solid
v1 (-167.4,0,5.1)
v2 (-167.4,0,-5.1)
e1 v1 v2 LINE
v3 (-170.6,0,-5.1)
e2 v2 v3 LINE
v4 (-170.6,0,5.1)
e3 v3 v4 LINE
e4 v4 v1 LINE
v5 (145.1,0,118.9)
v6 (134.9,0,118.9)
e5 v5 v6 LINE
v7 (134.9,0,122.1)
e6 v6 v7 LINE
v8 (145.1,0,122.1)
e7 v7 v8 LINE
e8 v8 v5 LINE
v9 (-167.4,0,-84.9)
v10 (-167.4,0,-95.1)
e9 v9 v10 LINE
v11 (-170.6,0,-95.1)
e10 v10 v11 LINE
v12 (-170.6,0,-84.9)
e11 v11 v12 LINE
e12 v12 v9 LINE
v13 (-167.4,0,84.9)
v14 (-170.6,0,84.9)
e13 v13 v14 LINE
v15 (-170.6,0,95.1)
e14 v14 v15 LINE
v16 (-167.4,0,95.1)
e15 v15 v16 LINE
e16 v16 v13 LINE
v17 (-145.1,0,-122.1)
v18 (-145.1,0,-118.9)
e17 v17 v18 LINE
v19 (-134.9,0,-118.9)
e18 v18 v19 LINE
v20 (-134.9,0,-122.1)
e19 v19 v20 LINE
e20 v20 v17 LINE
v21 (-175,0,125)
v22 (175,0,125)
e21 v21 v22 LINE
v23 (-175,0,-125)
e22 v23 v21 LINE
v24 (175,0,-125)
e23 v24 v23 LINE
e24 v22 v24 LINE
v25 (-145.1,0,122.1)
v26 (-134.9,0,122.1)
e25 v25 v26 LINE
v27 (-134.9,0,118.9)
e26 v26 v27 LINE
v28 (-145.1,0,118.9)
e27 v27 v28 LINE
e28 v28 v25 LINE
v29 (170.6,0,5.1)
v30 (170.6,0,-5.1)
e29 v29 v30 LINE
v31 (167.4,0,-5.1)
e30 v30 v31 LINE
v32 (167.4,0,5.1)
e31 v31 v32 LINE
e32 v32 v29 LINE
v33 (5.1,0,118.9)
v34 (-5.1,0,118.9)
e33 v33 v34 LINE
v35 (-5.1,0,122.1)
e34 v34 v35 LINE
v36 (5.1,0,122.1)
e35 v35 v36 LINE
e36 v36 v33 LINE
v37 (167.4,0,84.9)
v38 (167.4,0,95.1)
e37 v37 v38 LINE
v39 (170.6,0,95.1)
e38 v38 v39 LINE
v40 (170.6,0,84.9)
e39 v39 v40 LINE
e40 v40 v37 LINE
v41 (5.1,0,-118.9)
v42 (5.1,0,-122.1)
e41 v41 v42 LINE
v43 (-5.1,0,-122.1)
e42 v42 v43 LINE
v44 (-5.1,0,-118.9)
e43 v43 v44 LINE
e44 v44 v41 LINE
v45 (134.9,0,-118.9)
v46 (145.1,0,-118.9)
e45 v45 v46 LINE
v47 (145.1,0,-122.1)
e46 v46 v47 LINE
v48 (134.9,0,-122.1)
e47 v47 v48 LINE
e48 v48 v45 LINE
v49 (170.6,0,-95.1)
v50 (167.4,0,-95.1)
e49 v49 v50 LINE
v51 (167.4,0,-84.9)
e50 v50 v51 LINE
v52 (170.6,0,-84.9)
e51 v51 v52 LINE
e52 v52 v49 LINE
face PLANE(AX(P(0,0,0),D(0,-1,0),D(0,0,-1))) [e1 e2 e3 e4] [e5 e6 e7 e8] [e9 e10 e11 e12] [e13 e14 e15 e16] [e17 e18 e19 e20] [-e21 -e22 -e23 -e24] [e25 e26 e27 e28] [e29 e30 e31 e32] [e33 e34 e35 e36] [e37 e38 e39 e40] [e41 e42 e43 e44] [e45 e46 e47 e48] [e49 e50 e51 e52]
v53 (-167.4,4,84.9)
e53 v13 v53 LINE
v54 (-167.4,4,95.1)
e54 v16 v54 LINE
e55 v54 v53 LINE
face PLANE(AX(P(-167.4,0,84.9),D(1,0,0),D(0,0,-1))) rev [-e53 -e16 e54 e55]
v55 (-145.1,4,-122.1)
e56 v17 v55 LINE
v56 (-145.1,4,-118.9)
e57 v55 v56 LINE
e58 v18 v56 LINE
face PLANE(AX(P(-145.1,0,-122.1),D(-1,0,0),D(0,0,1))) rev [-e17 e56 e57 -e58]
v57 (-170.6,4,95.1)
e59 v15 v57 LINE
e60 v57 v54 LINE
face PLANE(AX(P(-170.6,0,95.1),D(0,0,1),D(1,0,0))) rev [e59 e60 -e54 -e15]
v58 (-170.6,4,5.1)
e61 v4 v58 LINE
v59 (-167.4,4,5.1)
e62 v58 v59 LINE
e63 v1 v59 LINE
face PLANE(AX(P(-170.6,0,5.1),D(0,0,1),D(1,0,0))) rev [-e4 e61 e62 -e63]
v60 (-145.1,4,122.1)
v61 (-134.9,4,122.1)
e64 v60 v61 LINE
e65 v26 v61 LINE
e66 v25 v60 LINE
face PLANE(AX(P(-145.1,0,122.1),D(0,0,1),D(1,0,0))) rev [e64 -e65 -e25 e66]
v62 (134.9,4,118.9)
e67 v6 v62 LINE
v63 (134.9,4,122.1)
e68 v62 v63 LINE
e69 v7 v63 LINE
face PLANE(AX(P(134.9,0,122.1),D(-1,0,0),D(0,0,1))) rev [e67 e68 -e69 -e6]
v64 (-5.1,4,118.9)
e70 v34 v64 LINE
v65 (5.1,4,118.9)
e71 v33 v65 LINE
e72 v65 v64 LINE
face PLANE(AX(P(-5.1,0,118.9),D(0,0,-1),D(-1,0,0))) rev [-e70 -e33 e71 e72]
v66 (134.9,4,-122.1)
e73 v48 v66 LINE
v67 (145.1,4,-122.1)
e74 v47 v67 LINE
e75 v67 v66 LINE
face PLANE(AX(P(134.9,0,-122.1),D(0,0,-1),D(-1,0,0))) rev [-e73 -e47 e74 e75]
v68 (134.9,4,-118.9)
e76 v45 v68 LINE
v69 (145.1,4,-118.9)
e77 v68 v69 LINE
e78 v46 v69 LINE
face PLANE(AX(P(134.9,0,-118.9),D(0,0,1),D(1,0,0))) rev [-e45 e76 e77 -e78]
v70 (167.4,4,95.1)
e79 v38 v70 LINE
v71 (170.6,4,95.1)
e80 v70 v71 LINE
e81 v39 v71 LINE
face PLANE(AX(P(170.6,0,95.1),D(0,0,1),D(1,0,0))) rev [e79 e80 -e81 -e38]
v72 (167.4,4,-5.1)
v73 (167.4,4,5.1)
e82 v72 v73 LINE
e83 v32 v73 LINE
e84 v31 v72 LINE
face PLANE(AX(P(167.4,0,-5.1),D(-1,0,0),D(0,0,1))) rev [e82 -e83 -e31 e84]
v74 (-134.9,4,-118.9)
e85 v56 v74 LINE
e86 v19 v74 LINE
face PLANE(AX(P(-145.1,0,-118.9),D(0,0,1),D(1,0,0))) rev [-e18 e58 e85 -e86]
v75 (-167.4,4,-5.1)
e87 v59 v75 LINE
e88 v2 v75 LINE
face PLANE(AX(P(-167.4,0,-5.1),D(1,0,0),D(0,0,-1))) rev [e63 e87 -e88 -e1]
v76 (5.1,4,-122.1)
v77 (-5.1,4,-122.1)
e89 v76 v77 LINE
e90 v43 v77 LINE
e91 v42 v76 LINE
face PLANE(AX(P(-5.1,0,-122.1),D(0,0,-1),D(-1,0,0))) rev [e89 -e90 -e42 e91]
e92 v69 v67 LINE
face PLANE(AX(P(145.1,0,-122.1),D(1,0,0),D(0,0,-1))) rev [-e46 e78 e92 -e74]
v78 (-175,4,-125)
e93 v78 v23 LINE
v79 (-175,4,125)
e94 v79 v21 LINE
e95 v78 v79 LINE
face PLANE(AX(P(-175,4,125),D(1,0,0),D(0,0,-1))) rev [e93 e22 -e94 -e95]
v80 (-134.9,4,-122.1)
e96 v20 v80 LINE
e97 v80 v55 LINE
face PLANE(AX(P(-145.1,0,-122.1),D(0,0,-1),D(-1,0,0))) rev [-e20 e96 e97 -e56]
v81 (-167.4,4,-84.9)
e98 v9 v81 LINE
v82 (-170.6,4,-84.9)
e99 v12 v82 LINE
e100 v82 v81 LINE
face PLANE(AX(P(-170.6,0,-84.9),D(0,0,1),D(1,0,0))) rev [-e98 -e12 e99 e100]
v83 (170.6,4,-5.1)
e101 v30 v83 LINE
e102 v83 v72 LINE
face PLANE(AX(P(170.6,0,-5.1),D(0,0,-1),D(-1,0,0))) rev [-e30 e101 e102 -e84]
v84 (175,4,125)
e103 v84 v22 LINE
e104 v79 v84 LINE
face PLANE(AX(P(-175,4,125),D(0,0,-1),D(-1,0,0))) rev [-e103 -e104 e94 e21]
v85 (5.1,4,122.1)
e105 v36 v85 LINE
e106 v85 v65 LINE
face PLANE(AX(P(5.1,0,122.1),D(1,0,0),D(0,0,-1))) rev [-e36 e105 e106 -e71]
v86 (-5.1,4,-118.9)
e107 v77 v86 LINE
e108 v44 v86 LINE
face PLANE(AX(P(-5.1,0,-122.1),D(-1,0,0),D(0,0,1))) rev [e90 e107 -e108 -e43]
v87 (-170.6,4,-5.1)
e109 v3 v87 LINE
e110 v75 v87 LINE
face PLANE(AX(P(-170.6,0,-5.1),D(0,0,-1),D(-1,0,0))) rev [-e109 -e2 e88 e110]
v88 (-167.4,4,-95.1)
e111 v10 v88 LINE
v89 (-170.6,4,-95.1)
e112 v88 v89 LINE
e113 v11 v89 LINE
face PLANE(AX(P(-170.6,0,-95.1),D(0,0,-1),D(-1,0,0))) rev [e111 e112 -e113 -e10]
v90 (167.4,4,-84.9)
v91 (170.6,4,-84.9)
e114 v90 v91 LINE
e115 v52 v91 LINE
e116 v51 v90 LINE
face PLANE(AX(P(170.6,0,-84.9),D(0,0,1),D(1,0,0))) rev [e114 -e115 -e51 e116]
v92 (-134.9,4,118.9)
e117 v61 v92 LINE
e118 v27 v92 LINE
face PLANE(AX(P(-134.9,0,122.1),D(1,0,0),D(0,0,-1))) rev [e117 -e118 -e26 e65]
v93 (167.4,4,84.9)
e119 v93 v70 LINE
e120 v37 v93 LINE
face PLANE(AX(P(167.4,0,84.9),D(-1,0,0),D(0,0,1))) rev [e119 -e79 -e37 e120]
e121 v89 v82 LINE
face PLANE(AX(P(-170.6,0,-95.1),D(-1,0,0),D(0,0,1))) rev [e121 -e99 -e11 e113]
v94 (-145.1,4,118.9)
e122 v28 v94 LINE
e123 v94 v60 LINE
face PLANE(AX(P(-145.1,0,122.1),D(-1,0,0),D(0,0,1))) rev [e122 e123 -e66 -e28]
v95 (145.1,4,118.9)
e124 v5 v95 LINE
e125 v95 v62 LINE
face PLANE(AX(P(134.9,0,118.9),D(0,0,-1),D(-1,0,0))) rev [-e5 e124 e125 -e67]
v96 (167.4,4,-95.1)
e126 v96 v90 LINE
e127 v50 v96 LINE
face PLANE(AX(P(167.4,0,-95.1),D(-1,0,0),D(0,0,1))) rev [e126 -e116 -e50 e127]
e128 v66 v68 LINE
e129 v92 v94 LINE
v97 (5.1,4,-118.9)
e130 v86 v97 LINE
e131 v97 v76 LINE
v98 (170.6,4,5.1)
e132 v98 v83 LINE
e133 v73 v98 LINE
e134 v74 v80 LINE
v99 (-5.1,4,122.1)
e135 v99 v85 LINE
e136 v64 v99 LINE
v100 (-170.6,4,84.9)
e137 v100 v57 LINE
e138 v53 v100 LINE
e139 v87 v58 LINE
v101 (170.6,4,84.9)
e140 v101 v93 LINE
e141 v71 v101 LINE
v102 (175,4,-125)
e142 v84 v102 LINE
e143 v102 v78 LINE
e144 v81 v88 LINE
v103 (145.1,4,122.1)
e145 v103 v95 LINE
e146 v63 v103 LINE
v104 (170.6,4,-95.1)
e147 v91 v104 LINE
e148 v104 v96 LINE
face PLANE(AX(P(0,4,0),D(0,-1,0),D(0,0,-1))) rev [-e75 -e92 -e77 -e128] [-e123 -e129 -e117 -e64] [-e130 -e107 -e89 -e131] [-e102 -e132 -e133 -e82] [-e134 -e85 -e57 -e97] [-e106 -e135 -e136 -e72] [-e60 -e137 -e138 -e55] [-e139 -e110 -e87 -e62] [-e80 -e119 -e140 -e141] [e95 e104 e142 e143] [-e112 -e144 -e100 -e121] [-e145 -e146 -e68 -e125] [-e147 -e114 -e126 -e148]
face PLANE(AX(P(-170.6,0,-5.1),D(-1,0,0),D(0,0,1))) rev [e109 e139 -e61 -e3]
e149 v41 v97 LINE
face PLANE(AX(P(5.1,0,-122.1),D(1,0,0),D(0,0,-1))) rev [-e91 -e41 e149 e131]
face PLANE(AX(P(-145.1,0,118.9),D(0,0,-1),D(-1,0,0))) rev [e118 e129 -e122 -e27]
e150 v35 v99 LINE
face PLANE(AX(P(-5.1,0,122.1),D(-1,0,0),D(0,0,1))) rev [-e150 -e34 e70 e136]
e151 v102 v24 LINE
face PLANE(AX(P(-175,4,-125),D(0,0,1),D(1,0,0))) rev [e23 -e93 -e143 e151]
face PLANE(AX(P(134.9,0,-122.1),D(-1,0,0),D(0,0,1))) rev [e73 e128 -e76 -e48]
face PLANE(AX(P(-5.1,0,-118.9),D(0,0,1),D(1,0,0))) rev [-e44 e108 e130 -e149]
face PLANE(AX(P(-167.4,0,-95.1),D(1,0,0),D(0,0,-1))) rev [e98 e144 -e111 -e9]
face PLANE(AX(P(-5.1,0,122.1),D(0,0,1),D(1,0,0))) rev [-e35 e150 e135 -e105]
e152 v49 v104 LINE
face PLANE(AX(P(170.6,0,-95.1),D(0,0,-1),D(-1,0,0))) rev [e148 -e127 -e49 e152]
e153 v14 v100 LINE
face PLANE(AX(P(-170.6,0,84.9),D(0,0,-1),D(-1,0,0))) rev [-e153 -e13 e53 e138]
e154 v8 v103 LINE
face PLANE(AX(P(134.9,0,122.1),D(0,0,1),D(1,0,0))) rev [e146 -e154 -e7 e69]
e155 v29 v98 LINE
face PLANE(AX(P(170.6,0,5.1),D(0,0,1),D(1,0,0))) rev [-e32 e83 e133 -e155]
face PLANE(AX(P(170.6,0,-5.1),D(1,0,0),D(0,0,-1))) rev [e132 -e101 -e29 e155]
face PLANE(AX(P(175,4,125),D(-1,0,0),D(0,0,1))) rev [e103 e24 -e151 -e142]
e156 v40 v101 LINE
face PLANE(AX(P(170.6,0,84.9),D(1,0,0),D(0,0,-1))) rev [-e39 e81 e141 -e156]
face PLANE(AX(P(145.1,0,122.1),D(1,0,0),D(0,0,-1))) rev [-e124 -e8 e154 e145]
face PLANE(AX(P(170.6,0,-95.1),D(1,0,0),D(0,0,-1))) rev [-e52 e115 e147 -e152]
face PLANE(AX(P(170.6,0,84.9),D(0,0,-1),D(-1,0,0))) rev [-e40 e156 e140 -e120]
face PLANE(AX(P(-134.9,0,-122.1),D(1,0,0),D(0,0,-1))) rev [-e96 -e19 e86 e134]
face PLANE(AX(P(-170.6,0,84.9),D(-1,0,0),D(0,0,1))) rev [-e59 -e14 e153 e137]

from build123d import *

# Parameters (mm, degrees)
SKETCH1_W           = 350
SKETCH1_H           = 250
BOSS_EXTRUDE1_DEPTH = 4
SKETCH2_W           = 3.2
SKETCH2_H           = 10.2
CUT_EXTRUDE1_DEPTH  = 216.095327704
SKETCH3_W           = 10.2
SKETCH3_H           = 3.2
CUT_EXTRUDE2_DEPTH  = 216.095327704


with BuildPart() as part:
    # Sketch1 → Boss-Extrude1 (new body)
    with BuildSketch(Plane(origin=(0, 0, 0), x_dir=(1, 0, 0), z_dir=(0, 1, 0))):
        Rectangle(SKETCH1_W, SKETCH1_H)
    extrude(amount=BOSS_EXTRUDE1_DEPTH)

    # Sketch2 → Cut-Extrude1 (cut, through all)
    with BuildSketch(Plane(origin=(0, 4, 0), x_dir=(1, 0, 0), z_dir=(0, 1, 0))):
        with Locations((-169, 90)):
            Rectangle(SKETCH2_W, SKETCH2_H)
        with Locations((-169, 0)):
            Rectangle(SKETCH2_W, SKETCH2_H)
        with Locations((-169, -90)):
            Rectangle(SKETCH2_W, SKETCH2_H)
        with Locations((169, -90)):
            Rectangle(SKETCH2_W, SKETCH2_H)
        with Locations((169, 0)):
            Rectangle(SKETCH2_W, SKETCH2_H)
        with Locations((169, 90)):
            Rectangle(SKETCH2_W, SKETCH2_H)
    extrude(amount=-CUT_EXTRUDE1_DEPTH, mode=Mode.SUBTRACT)

    # Sketch3 → Cut-Extrude2 (cut, through all)
    with BuildSketch(Plane(origin=(0, 4, 0), x_dir=(1, 0, 0), z_dir=(0, 1, 0))):
        with Locations((0, 120.5)):
            Rectangle(SKETCH3_W, SKETCH3_H)
        with Locations((140, 120.5)):
            Rectangle(SKETCH3_W, SKETCH3_H)
        with Locations((-140, 120.5)):
            Rectangle(SKETCH3_W, SKETCH3_H)
        with Locations((-140, -120.5)):
            Rectangle(SKETCH3_W, SKETCH3_H)
        with Locations((140, -120.5)):
            Rectangle(SKETCH3_W, SKETCH3_H)
        with Locations((0, -120.5)):
            Rectangle(SKETCH3_W, SKETCH3_H)
    extrude(amount=-CUT_EXTRUDE2_DEPTH, mode=Mode.SUBTRACT)


solid = part.part
